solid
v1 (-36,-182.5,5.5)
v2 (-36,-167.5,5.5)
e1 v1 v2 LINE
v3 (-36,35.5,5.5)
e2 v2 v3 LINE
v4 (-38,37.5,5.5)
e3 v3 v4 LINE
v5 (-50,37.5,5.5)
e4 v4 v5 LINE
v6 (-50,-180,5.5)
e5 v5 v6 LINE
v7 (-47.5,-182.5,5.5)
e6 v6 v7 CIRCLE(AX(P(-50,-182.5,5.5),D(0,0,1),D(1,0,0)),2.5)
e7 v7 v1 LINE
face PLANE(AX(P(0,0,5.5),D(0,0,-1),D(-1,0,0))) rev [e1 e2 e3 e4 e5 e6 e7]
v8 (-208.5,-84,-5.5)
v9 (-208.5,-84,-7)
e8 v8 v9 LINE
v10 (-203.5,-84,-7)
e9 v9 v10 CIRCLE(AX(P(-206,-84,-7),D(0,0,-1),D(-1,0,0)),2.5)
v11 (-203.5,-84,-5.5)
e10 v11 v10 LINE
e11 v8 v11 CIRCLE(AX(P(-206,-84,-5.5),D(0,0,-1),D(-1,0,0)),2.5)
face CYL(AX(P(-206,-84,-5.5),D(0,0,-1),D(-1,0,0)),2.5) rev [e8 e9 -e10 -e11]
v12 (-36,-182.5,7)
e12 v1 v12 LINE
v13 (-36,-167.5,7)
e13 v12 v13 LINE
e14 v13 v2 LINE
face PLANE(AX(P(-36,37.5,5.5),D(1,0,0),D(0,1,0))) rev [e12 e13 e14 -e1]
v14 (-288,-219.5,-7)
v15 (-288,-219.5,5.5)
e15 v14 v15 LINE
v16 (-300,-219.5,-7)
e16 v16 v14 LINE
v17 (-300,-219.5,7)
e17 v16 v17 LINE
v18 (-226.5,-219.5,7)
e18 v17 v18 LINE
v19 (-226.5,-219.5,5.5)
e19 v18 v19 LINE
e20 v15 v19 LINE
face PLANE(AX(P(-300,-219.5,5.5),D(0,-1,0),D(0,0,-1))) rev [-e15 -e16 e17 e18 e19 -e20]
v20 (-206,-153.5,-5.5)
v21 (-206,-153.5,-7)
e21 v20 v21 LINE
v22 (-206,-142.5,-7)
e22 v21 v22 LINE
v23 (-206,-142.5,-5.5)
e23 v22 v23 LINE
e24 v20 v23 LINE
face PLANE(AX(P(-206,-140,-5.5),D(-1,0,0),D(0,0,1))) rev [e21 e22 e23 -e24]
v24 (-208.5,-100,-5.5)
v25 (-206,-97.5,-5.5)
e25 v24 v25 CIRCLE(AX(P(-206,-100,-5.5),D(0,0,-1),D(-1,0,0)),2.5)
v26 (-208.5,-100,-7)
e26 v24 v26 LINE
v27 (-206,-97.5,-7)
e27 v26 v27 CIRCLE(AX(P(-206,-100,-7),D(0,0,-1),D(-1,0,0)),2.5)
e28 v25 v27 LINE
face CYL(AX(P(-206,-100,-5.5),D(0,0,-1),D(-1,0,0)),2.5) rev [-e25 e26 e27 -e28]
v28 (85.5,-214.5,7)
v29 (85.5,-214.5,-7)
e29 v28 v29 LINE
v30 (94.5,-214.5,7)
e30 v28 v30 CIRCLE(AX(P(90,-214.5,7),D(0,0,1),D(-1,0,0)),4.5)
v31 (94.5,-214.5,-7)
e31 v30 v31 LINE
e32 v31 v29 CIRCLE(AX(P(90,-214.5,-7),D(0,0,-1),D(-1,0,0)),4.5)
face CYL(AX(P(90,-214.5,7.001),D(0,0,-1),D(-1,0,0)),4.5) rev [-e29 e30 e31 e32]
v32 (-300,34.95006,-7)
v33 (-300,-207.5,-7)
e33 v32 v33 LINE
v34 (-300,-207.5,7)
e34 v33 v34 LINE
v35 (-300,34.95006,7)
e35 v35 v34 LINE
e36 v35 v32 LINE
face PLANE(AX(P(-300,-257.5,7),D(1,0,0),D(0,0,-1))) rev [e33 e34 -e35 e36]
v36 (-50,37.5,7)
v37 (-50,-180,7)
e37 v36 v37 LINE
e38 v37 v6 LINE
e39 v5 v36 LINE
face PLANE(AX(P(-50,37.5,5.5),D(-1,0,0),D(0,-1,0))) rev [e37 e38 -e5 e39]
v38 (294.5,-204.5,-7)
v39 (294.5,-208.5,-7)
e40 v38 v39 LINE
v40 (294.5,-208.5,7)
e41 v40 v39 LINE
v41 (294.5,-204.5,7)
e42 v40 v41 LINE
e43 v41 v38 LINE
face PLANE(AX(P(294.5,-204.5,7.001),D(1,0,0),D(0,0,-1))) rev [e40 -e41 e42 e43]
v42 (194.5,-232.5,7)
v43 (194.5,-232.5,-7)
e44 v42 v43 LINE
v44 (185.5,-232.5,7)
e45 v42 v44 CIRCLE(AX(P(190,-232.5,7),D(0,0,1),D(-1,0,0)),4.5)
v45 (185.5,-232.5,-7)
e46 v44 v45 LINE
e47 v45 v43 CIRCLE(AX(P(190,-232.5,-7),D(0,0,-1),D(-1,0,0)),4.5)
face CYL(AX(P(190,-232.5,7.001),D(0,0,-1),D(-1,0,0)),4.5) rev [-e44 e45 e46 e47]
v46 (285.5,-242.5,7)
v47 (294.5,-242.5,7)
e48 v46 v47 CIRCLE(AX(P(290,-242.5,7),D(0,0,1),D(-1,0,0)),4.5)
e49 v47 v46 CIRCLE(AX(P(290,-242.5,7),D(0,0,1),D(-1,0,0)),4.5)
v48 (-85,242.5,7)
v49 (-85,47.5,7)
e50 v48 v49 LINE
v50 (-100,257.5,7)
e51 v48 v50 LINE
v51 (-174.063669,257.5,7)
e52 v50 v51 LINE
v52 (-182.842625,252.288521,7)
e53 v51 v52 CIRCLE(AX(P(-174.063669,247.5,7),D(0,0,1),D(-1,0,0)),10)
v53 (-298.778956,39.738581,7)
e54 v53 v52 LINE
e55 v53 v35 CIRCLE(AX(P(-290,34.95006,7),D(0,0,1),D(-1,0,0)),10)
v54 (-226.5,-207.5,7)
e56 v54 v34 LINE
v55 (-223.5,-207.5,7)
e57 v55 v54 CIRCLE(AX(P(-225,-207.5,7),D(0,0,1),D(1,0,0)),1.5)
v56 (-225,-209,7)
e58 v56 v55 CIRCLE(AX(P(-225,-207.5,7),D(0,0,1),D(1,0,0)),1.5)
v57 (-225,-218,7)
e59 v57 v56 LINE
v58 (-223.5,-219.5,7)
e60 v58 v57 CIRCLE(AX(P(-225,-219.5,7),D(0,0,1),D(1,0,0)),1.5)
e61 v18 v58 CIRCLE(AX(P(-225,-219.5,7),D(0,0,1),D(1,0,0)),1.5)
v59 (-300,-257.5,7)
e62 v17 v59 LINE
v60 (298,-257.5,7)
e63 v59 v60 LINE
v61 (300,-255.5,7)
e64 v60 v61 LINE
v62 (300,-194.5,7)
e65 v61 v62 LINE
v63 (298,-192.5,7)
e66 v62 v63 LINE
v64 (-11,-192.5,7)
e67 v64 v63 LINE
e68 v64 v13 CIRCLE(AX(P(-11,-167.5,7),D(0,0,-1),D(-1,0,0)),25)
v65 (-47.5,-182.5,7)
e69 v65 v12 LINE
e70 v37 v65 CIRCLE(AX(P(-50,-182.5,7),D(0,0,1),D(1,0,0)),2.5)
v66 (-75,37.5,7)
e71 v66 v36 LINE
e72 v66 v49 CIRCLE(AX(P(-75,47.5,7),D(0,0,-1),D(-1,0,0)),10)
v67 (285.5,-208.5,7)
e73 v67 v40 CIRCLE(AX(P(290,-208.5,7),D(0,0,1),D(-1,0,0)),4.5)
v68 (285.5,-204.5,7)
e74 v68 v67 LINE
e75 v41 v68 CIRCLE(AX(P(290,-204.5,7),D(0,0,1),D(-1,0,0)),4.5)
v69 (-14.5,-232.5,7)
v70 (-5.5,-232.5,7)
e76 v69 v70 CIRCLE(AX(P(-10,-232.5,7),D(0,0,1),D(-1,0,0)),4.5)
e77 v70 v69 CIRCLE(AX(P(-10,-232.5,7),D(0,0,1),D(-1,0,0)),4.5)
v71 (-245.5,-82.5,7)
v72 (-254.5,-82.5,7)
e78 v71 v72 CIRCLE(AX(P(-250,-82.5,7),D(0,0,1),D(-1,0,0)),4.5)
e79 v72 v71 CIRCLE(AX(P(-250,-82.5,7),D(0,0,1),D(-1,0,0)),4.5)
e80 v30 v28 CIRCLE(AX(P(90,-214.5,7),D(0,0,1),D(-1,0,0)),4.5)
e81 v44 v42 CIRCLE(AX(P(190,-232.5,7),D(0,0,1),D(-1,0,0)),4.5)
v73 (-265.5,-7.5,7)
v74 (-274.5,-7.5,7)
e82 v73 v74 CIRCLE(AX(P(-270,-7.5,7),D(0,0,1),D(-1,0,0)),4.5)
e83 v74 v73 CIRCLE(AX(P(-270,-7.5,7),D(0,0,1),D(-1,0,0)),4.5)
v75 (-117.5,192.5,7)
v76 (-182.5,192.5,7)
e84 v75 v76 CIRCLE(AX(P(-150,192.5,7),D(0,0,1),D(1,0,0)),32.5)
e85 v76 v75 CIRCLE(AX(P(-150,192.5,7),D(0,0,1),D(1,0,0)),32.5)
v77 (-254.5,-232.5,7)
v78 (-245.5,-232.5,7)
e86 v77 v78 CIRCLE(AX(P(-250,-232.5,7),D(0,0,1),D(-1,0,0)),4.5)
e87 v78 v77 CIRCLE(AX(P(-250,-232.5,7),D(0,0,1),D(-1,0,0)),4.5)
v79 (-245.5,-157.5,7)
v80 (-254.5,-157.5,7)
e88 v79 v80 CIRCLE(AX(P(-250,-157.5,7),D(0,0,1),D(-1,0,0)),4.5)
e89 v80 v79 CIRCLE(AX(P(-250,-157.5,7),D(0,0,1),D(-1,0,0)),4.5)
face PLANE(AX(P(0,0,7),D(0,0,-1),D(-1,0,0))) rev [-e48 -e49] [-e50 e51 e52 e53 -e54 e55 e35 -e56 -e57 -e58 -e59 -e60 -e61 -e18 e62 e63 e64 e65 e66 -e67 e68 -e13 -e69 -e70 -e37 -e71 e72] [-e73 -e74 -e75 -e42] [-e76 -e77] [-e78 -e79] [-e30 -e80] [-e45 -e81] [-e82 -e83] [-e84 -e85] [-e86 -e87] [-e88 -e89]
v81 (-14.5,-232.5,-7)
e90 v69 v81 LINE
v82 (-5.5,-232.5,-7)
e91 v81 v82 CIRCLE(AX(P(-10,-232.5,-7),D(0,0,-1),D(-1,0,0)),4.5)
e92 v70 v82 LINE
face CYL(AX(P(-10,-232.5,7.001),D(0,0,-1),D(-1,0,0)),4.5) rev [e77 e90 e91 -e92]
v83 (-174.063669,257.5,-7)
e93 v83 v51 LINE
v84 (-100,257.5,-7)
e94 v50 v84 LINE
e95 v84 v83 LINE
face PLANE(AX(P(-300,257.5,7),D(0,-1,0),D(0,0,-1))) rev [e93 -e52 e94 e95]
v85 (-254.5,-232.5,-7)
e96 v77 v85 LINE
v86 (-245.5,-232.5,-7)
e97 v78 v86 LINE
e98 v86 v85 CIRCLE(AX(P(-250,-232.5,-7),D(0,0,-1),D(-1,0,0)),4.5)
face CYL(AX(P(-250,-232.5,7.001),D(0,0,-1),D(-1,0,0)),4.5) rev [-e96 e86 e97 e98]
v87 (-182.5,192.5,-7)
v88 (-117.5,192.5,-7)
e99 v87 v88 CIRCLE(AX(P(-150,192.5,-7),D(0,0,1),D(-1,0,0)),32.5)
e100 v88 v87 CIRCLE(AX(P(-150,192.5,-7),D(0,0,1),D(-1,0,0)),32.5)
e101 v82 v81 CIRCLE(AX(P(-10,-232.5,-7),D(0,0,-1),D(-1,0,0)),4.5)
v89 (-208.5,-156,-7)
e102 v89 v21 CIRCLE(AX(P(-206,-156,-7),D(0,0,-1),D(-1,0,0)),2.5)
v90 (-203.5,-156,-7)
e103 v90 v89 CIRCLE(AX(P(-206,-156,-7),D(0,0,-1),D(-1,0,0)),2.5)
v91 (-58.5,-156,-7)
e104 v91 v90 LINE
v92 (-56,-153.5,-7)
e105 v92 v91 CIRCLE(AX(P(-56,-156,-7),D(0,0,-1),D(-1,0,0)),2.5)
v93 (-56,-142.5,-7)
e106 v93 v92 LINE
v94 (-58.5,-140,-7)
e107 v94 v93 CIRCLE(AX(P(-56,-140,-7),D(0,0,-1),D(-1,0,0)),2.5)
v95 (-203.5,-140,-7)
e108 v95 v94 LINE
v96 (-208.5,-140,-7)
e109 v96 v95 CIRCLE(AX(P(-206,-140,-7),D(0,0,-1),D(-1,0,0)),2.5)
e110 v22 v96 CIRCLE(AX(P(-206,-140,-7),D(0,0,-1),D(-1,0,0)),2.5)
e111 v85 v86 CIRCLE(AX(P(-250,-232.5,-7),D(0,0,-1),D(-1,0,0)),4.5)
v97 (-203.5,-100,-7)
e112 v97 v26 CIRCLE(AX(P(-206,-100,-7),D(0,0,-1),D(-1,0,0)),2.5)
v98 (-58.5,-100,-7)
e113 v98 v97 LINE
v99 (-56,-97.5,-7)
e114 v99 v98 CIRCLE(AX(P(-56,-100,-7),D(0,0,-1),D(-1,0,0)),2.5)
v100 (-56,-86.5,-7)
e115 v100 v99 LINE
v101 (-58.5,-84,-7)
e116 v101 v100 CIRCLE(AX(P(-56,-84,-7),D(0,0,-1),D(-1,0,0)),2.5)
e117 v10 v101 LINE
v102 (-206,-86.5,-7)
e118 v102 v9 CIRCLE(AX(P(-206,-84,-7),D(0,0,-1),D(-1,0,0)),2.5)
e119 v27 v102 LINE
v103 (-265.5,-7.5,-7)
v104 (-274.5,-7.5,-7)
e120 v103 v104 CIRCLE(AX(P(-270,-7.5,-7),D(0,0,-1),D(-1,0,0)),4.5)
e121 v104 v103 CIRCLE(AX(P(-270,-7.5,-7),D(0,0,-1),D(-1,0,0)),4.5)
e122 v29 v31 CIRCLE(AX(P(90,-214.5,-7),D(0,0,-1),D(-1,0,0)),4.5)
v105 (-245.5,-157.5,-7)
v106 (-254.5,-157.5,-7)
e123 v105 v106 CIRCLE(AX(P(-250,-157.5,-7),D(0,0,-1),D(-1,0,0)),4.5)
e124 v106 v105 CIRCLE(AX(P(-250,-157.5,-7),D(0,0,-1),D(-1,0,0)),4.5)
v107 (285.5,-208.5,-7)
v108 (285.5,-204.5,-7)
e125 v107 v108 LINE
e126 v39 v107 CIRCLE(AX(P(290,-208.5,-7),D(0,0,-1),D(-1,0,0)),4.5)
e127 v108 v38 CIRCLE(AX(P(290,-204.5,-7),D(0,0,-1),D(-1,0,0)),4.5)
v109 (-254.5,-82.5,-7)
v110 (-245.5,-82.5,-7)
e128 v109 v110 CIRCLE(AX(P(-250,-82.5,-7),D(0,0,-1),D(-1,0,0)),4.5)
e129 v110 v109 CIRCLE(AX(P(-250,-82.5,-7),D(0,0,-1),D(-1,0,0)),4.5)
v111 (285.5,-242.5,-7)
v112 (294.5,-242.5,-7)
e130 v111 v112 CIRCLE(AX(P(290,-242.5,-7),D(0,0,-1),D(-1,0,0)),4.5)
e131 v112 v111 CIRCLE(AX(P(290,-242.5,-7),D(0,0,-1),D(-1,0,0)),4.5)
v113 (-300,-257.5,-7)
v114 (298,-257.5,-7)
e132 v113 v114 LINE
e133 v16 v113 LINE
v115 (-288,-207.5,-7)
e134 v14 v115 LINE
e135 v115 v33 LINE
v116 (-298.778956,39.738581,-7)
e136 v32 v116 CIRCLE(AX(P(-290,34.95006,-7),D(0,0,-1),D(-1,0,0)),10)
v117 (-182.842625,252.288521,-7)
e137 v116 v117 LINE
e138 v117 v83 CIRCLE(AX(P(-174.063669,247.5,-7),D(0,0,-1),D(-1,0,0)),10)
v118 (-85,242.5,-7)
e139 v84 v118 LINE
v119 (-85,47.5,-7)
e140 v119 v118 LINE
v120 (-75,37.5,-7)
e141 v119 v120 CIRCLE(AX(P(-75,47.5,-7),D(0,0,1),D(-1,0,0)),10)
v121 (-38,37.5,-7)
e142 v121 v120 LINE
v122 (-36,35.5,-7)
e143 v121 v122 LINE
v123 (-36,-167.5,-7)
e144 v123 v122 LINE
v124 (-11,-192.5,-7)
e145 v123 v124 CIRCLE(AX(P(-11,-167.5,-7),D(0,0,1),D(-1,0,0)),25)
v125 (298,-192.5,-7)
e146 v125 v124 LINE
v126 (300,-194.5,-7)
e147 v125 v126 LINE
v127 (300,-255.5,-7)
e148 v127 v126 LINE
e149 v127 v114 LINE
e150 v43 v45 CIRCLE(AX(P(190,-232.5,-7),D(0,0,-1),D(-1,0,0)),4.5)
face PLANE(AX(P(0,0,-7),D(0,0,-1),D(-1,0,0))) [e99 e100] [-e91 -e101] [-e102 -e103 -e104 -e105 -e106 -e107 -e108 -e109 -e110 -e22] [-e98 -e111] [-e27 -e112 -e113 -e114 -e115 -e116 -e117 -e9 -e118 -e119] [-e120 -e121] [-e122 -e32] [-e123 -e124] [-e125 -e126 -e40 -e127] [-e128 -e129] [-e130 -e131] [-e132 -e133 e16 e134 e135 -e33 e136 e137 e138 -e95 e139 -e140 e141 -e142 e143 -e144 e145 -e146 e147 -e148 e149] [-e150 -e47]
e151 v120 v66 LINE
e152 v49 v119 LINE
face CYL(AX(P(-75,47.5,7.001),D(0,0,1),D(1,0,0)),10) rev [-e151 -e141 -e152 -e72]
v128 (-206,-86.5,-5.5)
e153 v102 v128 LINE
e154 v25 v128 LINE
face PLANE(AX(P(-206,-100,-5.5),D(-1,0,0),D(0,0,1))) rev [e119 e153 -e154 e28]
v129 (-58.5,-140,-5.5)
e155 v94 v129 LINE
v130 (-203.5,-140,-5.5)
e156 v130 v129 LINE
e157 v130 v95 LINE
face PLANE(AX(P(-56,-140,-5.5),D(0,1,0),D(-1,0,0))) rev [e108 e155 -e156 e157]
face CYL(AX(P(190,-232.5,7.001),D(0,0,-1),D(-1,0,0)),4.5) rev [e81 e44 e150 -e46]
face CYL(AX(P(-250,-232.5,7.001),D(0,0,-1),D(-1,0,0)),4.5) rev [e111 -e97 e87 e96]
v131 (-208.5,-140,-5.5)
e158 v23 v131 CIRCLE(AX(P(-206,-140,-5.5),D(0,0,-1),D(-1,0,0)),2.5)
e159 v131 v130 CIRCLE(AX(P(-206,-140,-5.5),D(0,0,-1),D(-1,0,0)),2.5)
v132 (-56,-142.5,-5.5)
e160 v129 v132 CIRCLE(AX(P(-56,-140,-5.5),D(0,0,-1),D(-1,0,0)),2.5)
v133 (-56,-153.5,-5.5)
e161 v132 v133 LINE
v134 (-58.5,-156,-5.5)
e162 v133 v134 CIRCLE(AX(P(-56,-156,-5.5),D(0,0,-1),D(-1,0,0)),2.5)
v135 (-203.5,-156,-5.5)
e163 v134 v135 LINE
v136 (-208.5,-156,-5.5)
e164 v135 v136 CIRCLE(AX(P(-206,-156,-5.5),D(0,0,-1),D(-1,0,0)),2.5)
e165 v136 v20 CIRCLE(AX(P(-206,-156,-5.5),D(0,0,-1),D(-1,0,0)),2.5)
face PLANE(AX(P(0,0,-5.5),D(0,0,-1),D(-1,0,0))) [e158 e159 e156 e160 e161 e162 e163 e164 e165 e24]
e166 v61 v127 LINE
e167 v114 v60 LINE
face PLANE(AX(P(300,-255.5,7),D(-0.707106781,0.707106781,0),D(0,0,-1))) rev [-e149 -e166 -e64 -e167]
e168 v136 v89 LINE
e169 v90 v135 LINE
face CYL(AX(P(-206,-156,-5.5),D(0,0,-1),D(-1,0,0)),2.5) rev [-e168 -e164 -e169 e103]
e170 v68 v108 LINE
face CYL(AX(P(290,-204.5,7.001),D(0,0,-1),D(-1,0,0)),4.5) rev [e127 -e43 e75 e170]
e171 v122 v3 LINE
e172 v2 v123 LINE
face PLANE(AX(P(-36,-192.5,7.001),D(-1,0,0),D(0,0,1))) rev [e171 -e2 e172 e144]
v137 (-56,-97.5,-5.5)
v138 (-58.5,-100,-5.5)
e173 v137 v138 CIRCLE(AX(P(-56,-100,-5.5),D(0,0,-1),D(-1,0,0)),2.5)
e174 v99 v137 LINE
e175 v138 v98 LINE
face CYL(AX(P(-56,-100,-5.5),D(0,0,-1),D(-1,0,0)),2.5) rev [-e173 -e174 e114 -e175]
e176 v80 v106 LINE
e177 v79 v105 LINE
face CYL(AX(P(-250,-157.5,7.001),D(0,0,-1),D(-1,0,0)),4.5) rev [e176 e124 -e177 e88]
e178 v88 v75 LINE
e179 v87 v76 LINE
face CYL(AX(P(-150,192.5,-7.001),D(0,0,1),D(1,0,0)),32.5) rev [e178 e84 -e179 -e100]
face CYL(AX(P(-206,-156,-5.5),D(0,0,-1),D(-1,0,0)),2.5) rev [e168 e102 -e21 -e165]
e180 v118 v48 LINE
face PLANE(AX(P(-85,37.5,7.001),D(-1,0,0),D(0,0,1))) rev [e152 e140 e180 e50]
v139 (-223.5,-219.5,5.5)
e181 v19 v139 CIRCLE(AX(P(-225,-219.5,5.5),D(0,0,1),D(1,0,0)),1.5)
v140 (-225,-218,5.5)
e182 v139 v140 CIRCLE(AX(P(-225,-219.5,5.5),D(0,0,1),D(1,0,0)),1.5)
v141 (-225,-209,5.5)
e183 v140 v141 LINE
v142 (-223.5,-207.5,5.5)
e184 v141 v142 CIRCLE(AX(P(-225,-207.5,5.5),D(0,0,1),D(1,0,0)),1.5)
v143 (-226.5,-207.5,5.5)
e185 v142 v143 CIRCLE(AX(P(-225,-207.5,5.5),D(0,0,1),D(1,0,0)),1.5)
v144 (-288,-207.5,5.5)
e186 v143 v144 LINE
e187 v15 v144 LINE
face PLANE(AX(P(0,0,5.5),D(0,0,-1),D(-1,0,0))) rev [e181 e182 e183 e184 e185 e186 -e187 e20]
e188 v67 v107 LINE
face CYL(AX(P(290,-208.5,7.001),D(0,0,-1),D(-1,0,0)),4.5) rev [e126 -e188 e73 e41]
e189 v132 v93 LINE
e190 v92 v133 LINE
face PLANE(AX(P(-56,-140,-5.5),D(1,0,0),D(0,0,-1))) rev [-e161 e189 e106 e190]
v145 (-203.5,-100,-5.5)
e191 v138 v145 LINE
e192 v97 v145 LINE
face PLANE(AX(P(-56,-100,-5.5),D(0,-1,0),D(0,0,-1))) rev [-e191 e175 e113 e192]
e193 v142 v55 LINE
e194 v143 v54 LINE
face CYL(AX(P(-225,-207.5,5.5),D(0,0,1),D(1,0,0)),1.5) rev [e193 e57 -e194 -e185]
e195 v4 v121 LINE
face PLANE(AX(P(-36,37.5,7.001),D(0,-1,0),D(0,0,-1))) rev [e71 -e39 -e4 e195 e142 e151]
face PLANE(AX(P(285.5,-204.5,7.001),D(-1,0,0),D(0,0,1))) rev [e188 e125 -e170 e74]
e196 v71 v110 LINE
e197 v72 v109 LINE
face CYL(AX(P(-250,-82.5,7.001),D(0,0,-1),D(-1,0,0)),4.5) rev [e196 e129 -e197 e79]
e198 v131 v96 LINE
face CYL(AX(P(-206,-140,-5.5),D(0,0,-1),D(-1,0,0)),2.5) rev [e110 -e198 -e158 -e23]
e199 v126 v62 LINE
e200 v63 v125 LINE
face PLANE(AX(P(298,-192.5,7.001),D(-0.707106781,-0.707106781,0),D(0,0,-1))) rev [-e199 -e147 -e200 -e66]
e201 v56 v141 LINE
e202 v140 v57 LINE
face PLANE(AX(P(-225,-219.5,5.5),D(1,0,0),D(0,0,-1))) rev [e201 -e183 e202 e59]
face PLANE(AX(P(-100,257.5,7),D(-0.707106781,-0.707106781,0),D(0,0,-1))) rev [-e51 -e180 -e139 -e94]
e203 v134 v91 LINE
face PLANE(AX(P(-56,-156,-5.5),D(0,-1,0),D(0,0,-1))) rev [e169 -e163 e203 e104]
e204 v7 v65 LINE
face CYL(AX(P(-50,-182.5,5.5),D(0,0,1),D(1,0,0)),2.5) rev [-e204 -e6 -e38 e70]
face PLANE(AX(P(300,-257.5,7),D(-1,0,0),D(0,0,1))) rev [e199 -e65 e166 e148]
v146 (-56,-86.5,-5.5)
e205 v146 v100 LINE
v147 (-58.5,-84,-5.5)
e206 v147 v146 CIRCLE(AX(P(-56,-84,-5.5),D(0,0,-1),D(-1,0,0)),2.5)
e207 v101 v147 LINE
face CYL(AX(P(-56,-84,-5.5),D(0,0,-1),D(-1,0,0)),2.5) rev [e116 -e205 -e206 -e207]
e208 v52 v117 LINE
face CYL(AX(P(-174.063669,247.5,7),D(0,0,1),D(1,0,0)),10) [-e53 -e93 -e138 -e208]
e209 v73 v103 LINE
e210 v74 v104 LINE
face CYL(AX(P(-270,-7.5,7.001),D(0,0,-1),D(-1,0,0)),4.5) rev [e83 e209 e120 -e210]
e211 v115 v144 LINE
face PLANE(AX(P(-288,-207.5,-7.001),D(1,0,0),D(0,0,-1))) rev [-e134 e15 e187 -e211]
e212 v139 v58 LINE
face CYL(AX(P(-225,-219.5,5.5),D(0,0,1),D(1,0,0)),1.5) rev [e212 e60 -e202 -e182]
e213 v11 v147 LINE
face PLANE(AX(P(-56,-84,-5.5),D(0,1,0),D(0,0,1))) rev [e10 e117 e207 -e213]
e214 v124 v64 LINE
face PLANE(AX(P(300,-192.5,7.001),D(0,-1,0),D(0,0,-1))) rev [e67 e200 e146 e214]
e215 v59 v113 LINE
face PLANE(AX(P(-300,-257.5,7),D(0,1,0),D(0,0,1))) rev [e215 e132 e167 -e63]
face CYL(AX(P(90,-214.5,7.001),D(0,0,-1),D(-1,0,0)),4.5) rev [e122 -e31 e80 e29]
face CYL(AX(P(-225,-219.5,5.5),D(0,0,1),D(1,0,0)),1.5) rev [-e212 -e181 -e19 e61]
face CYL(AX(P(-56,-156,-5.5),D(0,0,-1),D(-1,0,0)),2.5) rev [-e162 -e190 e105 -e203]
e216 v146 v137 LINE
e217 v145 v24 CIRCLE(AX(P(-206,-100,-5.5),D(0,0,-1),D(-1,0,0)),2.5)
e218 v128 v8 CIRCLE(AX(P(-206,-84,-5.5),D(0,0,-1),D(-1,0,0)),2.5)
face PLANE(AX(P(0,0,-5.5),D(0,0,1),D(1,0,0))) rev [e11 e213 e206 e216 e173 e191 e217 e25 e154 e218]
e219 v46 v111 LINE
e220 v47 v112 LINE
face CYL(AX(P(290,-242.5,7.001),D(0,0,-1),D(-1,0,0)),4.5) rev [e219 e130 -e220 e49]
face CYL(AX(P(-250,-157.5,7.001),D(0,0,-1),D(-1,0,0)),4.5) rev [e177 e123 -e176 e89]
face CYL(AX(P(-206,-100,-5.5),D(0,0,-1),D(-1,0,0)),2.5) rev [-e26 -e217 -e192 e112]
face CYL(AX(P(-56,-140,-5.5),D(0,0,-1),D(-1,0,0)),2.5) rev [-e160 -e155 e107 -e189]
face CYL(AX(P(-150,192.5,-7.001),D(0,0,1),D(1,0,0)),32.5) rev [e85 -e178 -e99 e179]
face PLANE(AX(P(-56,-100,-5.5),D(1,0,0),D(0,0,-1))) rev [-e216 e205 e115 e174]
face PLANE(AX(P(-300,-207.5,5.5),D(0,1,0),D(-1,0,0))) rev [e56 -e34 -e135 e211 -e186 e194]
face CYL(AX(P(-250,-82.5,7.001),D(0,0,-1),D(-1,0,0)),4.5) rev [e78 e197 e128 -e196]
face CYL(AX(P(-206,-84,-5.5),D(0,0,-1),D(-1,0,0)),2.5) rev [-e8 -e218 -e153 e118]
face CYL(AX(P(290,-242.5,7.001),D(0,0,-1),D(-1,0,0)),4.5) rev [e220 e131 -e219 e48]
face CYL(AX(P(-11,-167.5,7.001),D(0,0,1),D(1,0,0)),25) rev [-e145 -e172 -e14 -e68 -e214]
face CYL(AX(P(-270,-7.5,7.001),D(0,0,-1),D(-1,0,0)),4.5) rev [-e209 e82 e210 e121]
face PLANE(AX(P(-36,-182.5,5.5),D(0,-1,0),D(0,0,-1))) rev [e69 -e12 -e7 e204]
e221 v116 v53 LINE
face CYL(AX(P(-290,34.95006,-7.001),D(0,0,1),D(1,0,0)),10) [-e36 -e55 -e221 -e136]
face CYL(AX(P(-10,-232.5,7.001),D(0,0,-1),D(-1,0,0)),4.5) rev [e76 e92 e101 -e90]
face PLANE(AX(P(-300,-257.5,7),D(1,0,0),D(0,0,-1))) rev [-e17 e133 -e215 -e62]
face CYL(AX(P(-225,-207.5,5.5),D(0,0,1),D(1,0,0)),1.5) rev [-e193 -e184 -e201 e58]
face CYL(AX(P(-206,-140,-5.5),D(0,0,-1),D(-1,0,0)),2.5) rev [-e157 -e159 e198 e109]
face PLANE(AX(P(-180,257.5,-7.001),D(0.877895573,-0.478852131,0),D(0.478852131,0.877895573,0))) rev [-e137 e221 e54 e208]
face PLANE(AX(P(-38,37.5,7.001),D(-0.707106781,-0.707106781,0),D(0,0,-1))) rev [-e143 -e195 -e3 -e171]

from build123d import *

# Parameters (mm, degrees)
SKETCH_1_W           = 600
SKETCH_1_H           = 515
EXTRUDE_1_DEPTH      = 7
CUT_EXTRUDE_1_REACH  = 397.604
SKETCH_2_R           = 32.5
CUT_EXTRUDE_2_REACH  = 397.604
SKETCH_3_R           = 4.5
SKETCH_4_W           = 150
SKETCH_4_H           = 16
CUT_EXTRUDE_3_DEPTH  = 1.5
SKETCH_5_R           = 2.5
CUT_EXTRUDE_4_DEPTH  = 1.5
SKETCH_6_W           = 75
SKETCH_6_H           = 12
CUT_EXTRUDE_5_DEPTH  = 1.5
SKETCH_7_R           = 1.5
CUT_EXTRUDE_6_DEPTH  = 1.5
CUT_EXTRUDE_7_REACH  = 397.553
SKETCH_8_W           = 12
SKETCH_8_H           = 12
CUT_EXTRUDE_8_REACH  = 397.604
SKETCH_9_R           = 4.5
CUT_EXTRUDE_9_REACH  = 397.604
FILLET_1_R           = 25
SKETCH_11_W          = 14
SKETCH_11_H          = 220
CUT_EXTRUDE_10_DEPTH = 1.5
SKETCH_12_R          = 2.5
CUT_EXTRUDE_11_DEPTH = 1.5
FILLET_2_R           = 10
CHAMFER_2_SIZE       = 2
CHAMFER_3_SIZE       = 2
CUT_EXTRUDE_12_REACH = 397.604
CHAMFER_4_SIZE       = 15
FILLET_3_R           = 10


with BuildPart() as part:
    # 草图1 → 凸台-拉伸1 (new, symmetric)
    with BuildSketch(Plane.XY):
        Rectangle(SKETCH_1_W, SKETCH_1_H)
    extrude(amount=EXTRUDE_1_DEPTH, both=True)

    # 草图2 → 切除-拉伸1 (cut, up to next)
    with BuildSketch(Plane.XY.offset(7), mode=Mode.PRIVATE) as cut_extrude_1_sk1:
        with Locations((-150, 192.5)):
            Circle(SKETCH_2_R)
    cut_extrude_1_tool1 = extrude(cut_extrude_1_sk1.sketch, amount=-CUT_EXTRUDE_1_REACH, mode=Mode.PRIVATE) & part.part
    add(cut_extrude_1_tool1.solids().sort_by_distance((-150, 192.5, 7))[0], mode=Mode.SUBTRACT)

    # 草图3 → 切除-拉伸2 (cut, up to next)
    with BuildSketch(Plane(origin=(0, 0, -7), x_dir=(-1, 0, 0), z_dir=(0, 0, -1)), mode=Mode.PRIVATE) as cut_extrude_2_sk1:
        with Locations((270, -7.5)):
            Circle(SKETCH_3_R)
    cut_extrude_2_tool1 = extrude(cut_extrude_2_sk1.sketch, amount=-CUT_EXTRUDE_2_REACH, mode=Mode.PRIVATE) & part.part
    # 草图3 → 切除-拉伸2 (cut, up to next)
    with BuildSketch(Plane(origin=(0, 0, -7), x_dir=(-1, 0, 0), z_dir=(0, 0, -1)), mode=Mode.PRIVATE) as cut_extrude_2_sk2:
        with Locations((250, -82.5)):
            Circle(SKETCH_3_R)
    cut_extrude_2_tool2 = extrude(cut_extrude_2_sk2.sketch, amount=-CUT_EXTRUDE_2_REACH, mode=Mode.PRIVATE) & part.part
    # 草图3 → 切除-拉伸2 (cut, up to next)
    with BuildSketch(Plane(origin=(0, 0, -7), x_dir=(-1, 0, 0), z_dir=(0, 0, -1)), mode=Mode.PRIVATE) as cut_extrude_2_sk3:
        with Locations((250, -157.5)):
            Circle(SKETCH_3_R)
    cut_extrude_2_tool3 = extrude(cut_extrude_2_sk3.sketch, amount=-CUT_EXTRUDE_2_REACH, mode=Mode.PRIVATE) & part.part
    # 草图3 → 切除-拉伸2 (cut, up to next)
    with BuildSketch(Plane(origin=(0, 0, -7), x_dir=(-1, 0, 0), z_dir=(0, 0, -1)), mode=Mode.PRIVATE) as cut_extrude_2_sk4:
        with Locations((250, -232.5)):
            Circle(SKETCH_3_R)
    cut_extrude_2_tool4 = extrude(cut_extrude_2_sk4.sketch, amount=-CUT_EXTRUDE_2_REACH, mode=Mode.PRIVATE) & part.part
    # 草图3 → 切除-拉伸2 (cut, up to next)
    with BuildSketch(Plane(origin=(0, 0, -7), x_dir=(-1, 0, 0), z_dir=(0, 0, -1)), mode=Mode.PRIVATE) as cut_extrude_2_sk5:
        with Locations((10, -232.5)):
            Circle(SKETCH_3_R)
    cut_extrude_2_tool5 = extrude(cut_extrude_2_sk5.sketch, amount=-CUT_EXTRUDE_2_REACH, mode=Mode.PRIVATE) & part.part
    add(cut_extrude_2_tool1.solids().sort_by_distance((-270, -7.5, -7))[0], mode=Mode.SUBTRACT)
    add(cut_extrude_2_tool2.solids().sort_by_distance((-250, -82.5, -7))[0], mode=Mode.SUBTRACT)
    add(cut_extrude_2_tool3.solids().sort_by_distance((-250, -157.5, -7))[0], mode=Mode.SUBTRACT)
    add(cut_extrude_2_tool4.solids().sort_by_distance((-250, -232.5, -7))[0], mode=Mode.SUBTRACT)
    add(cut_extrude_2_tool5.solids().sort_by_distance((-10, -232.5, -7))[0], mode=Mode.SUBTRACT)

    # 草图4 → 切除-拉伸3 (cut)
    with BuildSketch(Plane(origin=(0, 0, -7), x_dir=(-1, 0, 0), z_dir=(0, 0, -1))):
        with Locations((131, -92)):
            Rectangle(SKETCH_4_W, SKETCH_4_H)
        with Locations((131, -148)):
            Rectangle(SKETCH_4_W, SKETCH_4_H)
    extrude(amount=-CUT_EXTRUDE_3_DEPTH, mode=Mode.SUBTRACT)

    # 草图5 → 切除-拉伸4 (cut)
    with BuildSketch(Plane(origin=(0, 0, -7), x_dir=(-1, 0, 0), z_dir=(0, 0, -1))):
        with Locations((206, -84)):
            Circle(SKETCH_5_R)
        with Locations((206, -100)):
            Circle(SKETCH_5_R)
        with Locations((206, -140)):
            Circle(SKETCH_5_R)
        with Locations((206, -156)):
            Circle(SKETCH_5_R)
        with Locations((56, -84)):
            Circle(SKETCH_5_R)
        with Locations((56, -100)):
            Circle(SKETCH_5_R)
        with Locations((56, -140)):
            Circle(SKETCH_5_R)
        with Locations((56, -156)):
            Circle(SKETCH_5_R)
    extrude(amount=-CUT_EXTRUDE_4_DEPTH, mode=Mode.SUBTRACT)

    # 草图6 → 切除-拉伸5 (cut)
    with BuildSketch(Plane.XY.offset(7)):
        with Locations((-262.5, -213.5)):
            Rectangle(SKETCH_6_W, SKETCH_6_H)
    extrude(amount=-CUT_EXTRUDE_5_DEPTH, mode=Mode.SUBTRACT)

    # 草图7 → 切除-拉伸6 (cut)
    with BuildSketch(Plane.XY.offset(7)):
        with Locations((-225, -207.5)):
            Circle(SKETCH_7_R)
        with Locations((-225, -219.5)):
            Circle(SKETCH_7_R)
    extrude(amount=-CUT_EXTRUDE_6_DEPTH, mode=Mode.SUBTRACT)

    # 草图8 → 切除-拉伸7 (cut, up to next)
    with BuildSketch(Plane.XY.offset(5.5), mode=Mode.PRIVATE) as cut_extrude_7_sk1:
        with Locations((-294, -213.5)):
            Rectangle(SKETCH_8_W, SKETCH_8_H)
    cut_extrude_7_tool1 = extrude(cut_extrude_7_sk1.sketch, amount=-CUT_EXTRUDE_7_REACH, mode=Mode.PRIVATE) & part.part
    add(cut_extrude_7_tool1.solids().sort_by_distance((-294, -213.5, 5.5))[0], mode=Mode.SUBTRACT)

    # 草图9 → 切除-拉伸8 (cut, up to next)
    with BuildSketch(Plane(origin=(0, 0, -7), x_dir=(-1, 0, 0), z_dir=(0, 0, -1)), mode=Mode.PRIVATE) as cut_extrude_8_sk1:
        with Locations((-90, -214.5)):
            Circle(SKETCH_9_R)
    cut_extrude_8_tool1 = extrude(cut_extrude_8_sk1.sketch, amount=-CUT_EXTRUDE_8_REACH, mode=Mode.PRIVATE) & part.part
    # 草图9 → 切除-拉伸8 (cut, up to next)
    with BuildSketch(Plane(origin=(0, 0, -7), x_dir=(-1, 0, 0), z_dir=(0, 0, -1)), mode=Mode.PRIVATE) as cut_extrude_8_sk2:
        with Locations((-190, -232.5)):
            Circle(SKETCH_9_R)
    cut_extrude_8_tool2 = extrude(cut_extrude_8_sk2.sketch, amount=-CUT_EXTRUDE_8_REACH, mode=Mode.PRIVATE) & part.part
    # 草图9 → 切除-拉伸8 (cut, up to next)
    with BuildSketch(Plane(origin=(0, 0, -7), x_dir=(-1, 0, 0), z_dir=(0, 0, -1)), mode=Mode.PRIVATE) as cut_extrude_8_sk3:
        with Locations((-290, -242.5)):
            Circle(SKETCH_9_R)
    cut_extrude_8_tool3 = extrude(cut_extrude_8_sk3.sketch, amount=-CUT_EXTRUDE_8_REACH, mode=Mode.PRIVATE) & part.part
    # 草图9 → 切除-拉伸8 (cut, up to next)
    with BuildSketch(Plane(origin=(0, 0, -7), x_dir=(-1, 0, 0), z_dir=(0, 0, -1)), mode=Mode.PRIVATE) as cut_extrude_8_sk4:
        with BuildLine():
            Line((-285.5, -204.5), (-285.5, -208.5))
            ThreePointArc((-285.5, -208.5), (-290, -213), (-294.5, -208.5))
            Line((-294.5, -208.5), (-294.5, -204.5))
            ThreePointArc((-294.5, -204.5), (-290, -200), (-285.5, -204.5))
        make_face()
    cut_extrude_8_tool4 = extrude(cut_extrude_8_sk4.sketch, amount=-CUT_EXTRUDE_8_REACH, mode=Mode.PRIVATE) & part.part
    add(cut_extrude_8_tool1.solids().sort_by_distance((90, -214.5, -7))[0], mode=Mode.SUBTRACT)
    add(cut_extrude_8_tool2.solids().sort_by_distance((190, -232.5, -7))[0], mode=Mode.SUBTRACT)
    add(cut_extrude_8_tool3.solids().sort_by_distance((290, -242.5, -7))[0], mode=Mode.SUBTRACT)
    add(cut_extrude_8_tool4.solids().sort_by_distance((290, -206.5, -7))[0], mode=Mode.SUBTRACT)

    # 草图10 → 切除-拉伸9 (cut, up to next)
    with BuildSketch(Plane(origin=(0, 0, -7), x_dir=(-1, 0, 0), z_dir=(0, 0, -1)), mode=Mode.PRIVATE) as cut_extrude_9_sk1:
        Polygon((-300, 257.5), (-300, -192.5), (36, -192.5), (36, 37.5), (85, 37.5), (85, 257.5), align=None)
    cut_extrude_9_tool1 = extrude(cut_extrude_9_sk1.sketch, amount=-CUT_EXTRUDE_9_REACH, mode=Mode.PRIVATE) & part.part
    add(cut_extrude_9_tool1.solids().sort_by_distance((119.18885, 40.153414, -7))[0], mode=Mode.SUBTRACT)

    # 圆角1
    fillet_1_edges = [part.edges().sort_by_distance(p)[0] for p in [
        (-36, -192.5, 0),
    ]]
    fillet(fillet_1_edges, radius=FILLET_1_R)

    # 草图11 → 切除-拉伸10 (cut)
    with BuildSketch(Plane.XY.offset(7)):
        with Locations((-43, -72.5)):
            Rectangle(SKETCH_11_W, SKETCH_11_H)
    extrude(amount=-CUT_EXTRUDE_10_DEPTH, mode=Mode.SUBTRACT)

    # 草图12 → 切除-拉伸11 (cut)
    with BuildSketch(Plane.XY.offset(7)):
        with Locations((-50, -182.5)):
            Circle(SKETCH_12_R)
    extrude(amount=-CUT_EXTRUDE_11_DEPTH, mode=Mode.SUBTRACT)

    # 圆角2
    fillet_2_edges = [part.edges().sort_by_distance(p)[0] for p in [
        (-85, 37.5, 0),
    ]]
    fillet(fillet_2_edges, radius=FILLET_2_R)

    # 倒角2
    chamfer_2_edges = [part.edges().sort_by_distance(p)[0] for p in [
        (-36, 37.5, -0.75),
    ]]
    chamfer(chamfer_2_edges, length=CHAMFER_2_SIZE)

    # 倒角3
    chamfer_3_edges = [part.edges().sort_by_distance(p)[0] for p in [
        (300, -192.5, 0),
        (300, -257.5, 0),
    ]]
    chamfer(chamfer_3_edges, length=CHAMFER_3_SIZE)

    # 草图13 → 切除-拉伸12 (cut, up to next)
    with BuildSketch(Plane.XY.offset(7), mode=Mode.PRIVATE) as cut_extrude_12_sk1:
        Polygon((-180, 257.5), (-300, 37.5), (-300, 257.5), align=None)
    cut_extrude_12_tool1 = extrude(cut_extrude_12_sk1.sketch, amount=-CUT_EXTRUDE_12_REACH, mode=Mode.PRIVATE) & part.part
    add(cut_extrude_12_tool1.solids().sort_by_distance((-260, 184.166667, 7))[0], mode=Mode.SUBTRACT)

    # 倒角4
    chamfer_4_edges = [part.edges().sort_by_distance(p)[0] for p in [
        (-85, 257.5, 0),
    ]]
    chamfer(chamfer_4_edges, length=CHAMFER_4_SIZE)

    # 圆角3
    fillet_3_edges = [part.edges().sort_by_distance(p)[0] for p in [
        (-180, 257.5, 0),
        (-300, 37.5, 0),
    ]]
    fillet(fillet_3_edges, radius=FILLET_3_R)


solid = part.part
